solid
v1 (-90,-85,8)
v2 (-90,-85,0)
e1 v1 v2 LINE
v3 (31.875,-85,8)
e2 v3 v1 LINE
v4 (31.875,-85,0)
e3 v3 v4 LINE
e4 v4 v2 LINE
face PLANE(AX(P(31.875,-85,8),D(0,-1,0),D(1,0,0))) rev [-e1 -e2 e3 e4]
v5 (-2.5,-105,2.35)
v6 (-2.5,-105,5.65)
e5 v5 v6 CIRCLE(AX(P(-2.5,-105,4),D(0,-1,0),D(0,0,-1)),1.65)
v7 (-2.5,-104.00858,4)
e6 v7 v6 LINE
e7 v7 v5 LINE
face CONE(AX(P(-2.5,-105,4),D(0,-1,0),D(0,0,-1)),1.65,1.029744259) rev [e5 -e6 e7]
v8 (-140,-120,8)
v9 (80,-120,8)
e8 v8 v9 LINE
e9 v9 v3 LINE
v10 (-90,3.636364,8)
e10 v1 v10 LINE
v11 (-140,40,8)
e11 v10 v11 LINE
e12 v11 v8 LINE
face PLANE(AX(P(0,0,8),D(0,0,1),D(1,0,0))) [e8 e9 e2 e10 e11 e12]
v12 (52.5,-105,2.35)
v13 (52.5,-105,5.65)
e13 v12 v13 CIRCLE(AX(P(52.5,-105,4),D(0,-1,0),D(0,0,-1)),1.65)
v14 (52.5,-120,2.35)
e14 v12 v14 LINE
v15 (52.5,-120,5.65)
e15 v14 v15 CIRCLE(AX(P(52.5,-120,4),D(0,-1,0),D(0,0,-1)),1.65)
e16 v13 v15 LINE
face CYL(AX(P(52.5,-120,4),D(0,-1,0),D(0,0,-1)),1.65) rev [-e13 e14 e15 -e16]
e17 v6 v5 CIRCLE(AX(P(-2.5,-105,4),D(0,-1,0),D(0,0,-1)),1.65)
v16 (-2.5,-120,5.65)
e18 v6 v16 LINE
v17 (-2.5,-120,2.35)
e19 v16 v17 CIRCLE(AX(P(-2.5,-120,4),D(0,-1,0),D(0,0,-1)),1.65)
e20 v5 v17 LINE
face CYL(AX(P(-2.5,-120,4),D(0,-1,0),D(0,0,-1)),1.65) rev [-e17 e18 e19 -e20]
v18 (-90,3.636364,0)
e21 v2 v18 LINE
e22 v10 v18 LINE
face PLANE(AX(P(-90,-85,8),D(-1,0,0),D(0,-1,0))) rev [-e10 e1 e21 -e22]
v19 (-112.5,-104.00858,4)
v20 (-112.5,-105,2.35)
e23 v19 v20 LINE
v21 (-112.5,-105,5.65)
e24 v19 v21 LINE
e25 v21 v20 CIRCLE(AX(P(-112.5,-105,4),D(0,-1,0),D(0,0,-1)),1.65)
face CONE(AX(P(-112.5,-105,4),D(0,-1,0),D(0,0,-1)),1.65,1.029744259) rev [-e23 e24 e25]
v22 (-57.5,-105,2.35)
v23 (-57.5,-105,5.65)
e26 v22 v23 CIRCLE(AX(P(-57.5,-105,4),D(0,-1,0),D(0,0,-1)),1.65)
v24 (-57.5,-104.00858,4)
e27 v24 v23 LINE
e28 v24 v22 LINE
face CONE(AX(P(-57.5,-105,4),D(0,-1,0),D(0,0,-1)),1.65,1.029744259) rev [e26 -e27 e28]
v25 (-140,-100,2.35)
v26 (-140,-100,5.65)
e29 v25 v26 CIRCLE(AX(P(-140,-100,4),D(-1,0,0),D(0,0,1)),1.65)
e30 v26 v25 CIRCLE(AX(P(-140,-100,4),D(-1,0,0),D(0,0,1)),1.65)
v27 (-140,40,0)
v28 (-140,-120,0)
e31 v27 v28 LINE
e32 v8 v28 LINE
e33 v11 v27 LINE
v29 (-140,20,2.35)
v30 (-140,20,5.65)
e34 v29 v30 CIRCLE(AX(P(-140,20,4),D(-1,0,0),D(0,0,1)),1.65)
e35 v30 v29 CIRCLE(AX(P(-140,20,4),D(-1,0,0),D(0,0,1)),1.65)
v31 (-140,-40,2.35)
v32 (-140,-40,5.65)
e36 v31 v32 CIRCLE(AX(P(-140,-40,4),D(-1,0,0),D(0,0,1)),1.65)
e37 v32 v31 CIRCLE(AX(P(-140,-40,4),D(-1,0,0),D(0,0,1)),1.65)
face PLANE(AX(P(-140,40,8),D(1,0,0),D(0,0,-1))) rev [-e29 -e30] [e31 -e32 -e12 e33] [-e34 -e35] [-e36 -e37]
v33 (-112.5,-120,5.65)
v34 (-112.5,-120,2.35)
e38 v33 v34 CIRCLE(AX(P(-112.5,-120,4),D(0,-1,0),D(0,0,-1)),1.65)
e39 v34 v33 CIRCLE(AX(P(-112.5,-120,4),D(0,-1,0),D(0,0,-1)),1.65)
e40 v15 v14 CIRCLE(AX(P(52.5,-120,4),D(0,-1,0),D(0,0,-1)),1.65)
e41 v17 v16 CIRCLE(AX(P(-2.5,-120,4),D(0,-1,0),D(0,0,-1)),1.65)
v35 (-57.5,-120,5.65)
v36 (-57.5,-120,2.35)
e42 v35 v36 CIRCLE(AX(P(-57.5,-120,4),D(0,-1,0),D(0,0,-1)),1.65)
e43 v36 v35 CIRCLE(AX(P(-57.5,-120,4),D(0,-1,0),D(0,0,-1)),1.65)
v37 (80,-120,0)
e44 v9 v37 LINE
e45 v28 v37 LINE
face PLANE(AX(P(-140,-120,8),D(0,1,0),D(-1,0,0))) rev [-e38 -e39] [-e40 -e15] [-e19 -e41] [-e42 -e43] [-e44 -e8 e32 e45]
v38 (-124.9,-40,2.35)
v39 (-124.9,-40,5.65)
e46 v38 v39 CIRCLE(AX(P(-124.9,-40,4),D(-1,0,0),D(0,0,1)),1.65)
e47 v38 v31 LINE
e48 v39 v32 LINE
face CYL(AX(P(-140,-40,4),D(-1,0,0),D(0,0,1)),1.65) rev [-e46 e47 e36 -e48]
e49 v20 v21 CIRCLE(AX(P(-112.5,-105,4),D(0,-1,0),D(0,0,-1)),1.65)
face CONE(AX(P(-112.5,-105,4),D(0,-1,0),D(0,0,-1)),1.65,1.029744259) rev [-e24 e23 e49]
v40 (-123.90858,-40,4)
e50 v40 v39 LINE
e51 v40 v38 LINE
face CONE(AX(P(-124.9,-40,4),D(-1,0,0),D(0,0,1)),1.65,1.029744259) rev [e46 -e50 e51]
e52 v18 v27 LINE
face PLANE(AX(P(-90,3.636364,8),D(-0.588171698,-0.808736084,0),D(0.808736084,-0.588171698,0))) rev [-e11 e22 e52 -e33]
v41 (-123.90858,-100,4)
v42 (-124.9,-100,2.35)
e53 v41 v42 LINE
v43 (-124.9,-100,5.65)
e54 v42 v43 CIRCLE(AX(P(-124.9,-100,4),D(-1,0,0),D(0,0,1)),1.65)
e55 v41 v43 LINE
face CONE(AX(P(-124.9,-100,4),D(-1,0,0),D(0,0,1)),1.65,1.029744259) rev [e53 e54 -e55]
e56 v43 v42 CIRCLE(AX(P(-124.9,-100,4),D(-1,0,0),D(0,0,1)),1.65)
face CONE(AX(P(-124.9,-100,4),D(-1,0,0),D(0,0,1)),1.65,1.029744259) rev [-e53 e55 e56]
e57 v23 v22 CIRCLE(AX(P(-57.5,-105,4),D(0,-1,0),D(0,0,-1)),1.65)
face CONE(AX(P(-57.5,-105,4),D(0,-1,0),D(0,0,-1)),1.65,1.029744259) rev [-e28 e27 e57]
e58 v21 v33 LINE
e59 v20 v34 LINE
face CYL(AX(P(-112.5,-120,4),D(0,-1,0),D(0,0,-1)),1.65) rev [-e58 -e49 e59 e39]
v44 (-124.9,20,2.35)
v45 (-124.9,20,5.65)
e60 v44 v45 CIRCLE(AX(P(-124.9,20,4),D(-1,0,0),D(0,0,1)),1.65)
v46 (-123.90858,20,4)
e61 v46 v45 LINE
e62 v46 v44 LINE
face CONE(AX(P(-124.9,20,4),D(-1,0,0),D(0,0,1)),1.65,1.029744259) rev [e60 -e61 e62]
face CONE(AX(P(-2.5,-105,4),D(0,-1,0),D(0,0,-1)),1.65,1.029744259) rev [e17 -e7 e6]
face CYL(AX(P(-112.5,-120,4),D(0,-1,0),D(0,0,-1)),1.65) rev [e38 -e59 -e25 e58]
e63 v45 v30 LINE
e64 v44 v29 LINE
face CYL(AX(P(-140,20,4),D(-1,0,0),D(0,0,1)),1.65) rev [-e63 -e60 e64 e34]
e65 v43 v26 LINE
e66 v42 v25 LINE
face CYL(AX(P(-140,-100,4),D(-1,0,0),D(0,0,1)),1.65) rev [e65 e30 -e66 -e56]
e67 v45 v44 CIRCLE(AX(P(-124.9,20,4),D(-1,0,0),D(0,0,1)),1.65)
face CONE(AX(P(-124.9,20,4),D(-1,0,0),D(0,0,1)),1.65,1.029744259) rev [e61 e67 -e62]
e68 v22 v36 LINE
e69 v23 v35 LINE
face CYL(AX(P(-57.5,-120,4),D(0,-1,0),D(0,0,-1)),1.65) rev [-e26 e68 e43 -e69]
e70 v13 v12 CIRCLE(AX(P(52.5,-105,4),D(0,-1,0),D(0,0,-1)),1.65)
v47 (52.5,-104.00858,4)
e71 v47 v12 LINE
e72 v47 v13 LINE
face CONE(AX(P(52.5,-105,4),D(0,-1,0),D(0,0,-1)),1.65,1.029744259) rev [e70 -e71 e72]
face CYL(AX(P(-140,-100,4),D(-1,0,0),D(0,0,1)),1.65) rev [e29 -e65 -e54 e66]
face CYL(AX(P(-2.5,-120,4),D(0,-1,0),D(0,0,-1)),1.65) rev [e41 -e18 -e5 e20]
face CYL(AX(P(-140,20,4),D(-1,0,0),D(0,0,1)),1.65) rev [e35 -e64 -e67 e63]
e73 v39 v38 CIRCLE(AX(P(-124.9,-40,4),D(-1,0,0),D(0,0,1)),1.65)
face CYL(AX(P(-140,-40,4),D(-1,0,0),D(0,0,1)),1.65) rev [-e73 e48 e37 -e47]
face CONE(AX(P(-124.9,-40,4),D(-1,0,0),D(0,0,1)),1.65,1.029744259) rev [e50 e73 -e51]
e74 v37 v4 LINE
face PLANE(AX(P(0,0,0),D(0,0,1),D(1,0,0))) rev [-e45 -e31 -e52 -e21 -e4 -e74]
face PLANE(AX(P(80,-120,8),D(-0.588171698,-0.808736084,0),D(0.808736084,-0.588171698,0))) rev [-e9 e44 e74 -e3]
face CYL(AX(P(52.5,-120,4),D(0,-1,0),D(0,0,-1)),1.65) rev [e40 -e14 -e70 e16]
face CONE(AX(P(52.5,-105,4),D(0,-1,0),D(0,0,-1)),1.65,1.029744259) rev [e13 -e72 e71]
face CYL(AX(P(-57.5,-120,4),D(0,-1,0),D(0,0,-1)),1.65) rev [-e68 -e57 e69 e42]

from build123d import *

# Parameters (mm, degrees)
EXTRUDE_1_DEPTH        = 8
HOLE_WIZARD_M4_1_D     = 3.3
HOLE_WIZARD_M4_1_DEPTH = 15
HOLE_WIZARD_M4_1_TIP   = 0.991420021
HOLE_WIZARD_M4_2_D     = 3.3
HOLE_WIZARD_M4_2_DEPTH = 15.1
HOLE_WIZARD_M4_2_TIP   = 0.991420021


with BuildPart() as part:
    # 草图1 → 凸台-拉伸1 (new body)
    with BuildSketch(Plane.XY):
        Polygon((-140, 40), (-140, -120), (80, -120), (31.875, -85), (-90, -85), (-90, 3.636363636), align=None)
    extrude(amount=EXTRUDE_1_DEPTH)

    # M4 螺纹孔1
    with Locations(Plane(origin=(0, -120, 0), x_dir=(-1, 0, 0), z_dir=(0, -1, 0))):
        with Locations((112.5, -4), (57.5, -4), (2.5, -4), (-52.5, -4)):
            Hole(HOLE_WIZARD_M4_1_D / 2, depth=HOLE_WIZARD_M4_1_DEPTH)
            with Locations((0, 0, -(HOLE_WIZARD_M4_1_DEPTH + HOLE_WIZARD_M4_1_TIP / 2))):  # 118° drill point
                Cone(0, HOLE_WIZARD_M4_1_D / 2, HOLE_WIZARD_M4_1_TIP, mode=Mode.SUBTRACT)

    # M4 螺纹孔2
    with Locations(Plane.ZY.offset(140)):
        with Locations((4, 20), (4, -40), (4, -100)):
            Hole(HOLE_WIZARD_M4_2_D / 2, depth=HOLE_WIZARD_M4_2_DEPTH)
            with Locations((0, 0, -(HOLE_WIZARD_M4_2_DEPTH + HOLE_WIZARD_M4_2_TIP / 2))):  # 118° drill point
                Cone(0, HOLE_WIZARD_M4_2_D / 2, HOLE_WIZARD_M4_2_TIP, mode=Mode.SUBTRACT)


solid = part.part
